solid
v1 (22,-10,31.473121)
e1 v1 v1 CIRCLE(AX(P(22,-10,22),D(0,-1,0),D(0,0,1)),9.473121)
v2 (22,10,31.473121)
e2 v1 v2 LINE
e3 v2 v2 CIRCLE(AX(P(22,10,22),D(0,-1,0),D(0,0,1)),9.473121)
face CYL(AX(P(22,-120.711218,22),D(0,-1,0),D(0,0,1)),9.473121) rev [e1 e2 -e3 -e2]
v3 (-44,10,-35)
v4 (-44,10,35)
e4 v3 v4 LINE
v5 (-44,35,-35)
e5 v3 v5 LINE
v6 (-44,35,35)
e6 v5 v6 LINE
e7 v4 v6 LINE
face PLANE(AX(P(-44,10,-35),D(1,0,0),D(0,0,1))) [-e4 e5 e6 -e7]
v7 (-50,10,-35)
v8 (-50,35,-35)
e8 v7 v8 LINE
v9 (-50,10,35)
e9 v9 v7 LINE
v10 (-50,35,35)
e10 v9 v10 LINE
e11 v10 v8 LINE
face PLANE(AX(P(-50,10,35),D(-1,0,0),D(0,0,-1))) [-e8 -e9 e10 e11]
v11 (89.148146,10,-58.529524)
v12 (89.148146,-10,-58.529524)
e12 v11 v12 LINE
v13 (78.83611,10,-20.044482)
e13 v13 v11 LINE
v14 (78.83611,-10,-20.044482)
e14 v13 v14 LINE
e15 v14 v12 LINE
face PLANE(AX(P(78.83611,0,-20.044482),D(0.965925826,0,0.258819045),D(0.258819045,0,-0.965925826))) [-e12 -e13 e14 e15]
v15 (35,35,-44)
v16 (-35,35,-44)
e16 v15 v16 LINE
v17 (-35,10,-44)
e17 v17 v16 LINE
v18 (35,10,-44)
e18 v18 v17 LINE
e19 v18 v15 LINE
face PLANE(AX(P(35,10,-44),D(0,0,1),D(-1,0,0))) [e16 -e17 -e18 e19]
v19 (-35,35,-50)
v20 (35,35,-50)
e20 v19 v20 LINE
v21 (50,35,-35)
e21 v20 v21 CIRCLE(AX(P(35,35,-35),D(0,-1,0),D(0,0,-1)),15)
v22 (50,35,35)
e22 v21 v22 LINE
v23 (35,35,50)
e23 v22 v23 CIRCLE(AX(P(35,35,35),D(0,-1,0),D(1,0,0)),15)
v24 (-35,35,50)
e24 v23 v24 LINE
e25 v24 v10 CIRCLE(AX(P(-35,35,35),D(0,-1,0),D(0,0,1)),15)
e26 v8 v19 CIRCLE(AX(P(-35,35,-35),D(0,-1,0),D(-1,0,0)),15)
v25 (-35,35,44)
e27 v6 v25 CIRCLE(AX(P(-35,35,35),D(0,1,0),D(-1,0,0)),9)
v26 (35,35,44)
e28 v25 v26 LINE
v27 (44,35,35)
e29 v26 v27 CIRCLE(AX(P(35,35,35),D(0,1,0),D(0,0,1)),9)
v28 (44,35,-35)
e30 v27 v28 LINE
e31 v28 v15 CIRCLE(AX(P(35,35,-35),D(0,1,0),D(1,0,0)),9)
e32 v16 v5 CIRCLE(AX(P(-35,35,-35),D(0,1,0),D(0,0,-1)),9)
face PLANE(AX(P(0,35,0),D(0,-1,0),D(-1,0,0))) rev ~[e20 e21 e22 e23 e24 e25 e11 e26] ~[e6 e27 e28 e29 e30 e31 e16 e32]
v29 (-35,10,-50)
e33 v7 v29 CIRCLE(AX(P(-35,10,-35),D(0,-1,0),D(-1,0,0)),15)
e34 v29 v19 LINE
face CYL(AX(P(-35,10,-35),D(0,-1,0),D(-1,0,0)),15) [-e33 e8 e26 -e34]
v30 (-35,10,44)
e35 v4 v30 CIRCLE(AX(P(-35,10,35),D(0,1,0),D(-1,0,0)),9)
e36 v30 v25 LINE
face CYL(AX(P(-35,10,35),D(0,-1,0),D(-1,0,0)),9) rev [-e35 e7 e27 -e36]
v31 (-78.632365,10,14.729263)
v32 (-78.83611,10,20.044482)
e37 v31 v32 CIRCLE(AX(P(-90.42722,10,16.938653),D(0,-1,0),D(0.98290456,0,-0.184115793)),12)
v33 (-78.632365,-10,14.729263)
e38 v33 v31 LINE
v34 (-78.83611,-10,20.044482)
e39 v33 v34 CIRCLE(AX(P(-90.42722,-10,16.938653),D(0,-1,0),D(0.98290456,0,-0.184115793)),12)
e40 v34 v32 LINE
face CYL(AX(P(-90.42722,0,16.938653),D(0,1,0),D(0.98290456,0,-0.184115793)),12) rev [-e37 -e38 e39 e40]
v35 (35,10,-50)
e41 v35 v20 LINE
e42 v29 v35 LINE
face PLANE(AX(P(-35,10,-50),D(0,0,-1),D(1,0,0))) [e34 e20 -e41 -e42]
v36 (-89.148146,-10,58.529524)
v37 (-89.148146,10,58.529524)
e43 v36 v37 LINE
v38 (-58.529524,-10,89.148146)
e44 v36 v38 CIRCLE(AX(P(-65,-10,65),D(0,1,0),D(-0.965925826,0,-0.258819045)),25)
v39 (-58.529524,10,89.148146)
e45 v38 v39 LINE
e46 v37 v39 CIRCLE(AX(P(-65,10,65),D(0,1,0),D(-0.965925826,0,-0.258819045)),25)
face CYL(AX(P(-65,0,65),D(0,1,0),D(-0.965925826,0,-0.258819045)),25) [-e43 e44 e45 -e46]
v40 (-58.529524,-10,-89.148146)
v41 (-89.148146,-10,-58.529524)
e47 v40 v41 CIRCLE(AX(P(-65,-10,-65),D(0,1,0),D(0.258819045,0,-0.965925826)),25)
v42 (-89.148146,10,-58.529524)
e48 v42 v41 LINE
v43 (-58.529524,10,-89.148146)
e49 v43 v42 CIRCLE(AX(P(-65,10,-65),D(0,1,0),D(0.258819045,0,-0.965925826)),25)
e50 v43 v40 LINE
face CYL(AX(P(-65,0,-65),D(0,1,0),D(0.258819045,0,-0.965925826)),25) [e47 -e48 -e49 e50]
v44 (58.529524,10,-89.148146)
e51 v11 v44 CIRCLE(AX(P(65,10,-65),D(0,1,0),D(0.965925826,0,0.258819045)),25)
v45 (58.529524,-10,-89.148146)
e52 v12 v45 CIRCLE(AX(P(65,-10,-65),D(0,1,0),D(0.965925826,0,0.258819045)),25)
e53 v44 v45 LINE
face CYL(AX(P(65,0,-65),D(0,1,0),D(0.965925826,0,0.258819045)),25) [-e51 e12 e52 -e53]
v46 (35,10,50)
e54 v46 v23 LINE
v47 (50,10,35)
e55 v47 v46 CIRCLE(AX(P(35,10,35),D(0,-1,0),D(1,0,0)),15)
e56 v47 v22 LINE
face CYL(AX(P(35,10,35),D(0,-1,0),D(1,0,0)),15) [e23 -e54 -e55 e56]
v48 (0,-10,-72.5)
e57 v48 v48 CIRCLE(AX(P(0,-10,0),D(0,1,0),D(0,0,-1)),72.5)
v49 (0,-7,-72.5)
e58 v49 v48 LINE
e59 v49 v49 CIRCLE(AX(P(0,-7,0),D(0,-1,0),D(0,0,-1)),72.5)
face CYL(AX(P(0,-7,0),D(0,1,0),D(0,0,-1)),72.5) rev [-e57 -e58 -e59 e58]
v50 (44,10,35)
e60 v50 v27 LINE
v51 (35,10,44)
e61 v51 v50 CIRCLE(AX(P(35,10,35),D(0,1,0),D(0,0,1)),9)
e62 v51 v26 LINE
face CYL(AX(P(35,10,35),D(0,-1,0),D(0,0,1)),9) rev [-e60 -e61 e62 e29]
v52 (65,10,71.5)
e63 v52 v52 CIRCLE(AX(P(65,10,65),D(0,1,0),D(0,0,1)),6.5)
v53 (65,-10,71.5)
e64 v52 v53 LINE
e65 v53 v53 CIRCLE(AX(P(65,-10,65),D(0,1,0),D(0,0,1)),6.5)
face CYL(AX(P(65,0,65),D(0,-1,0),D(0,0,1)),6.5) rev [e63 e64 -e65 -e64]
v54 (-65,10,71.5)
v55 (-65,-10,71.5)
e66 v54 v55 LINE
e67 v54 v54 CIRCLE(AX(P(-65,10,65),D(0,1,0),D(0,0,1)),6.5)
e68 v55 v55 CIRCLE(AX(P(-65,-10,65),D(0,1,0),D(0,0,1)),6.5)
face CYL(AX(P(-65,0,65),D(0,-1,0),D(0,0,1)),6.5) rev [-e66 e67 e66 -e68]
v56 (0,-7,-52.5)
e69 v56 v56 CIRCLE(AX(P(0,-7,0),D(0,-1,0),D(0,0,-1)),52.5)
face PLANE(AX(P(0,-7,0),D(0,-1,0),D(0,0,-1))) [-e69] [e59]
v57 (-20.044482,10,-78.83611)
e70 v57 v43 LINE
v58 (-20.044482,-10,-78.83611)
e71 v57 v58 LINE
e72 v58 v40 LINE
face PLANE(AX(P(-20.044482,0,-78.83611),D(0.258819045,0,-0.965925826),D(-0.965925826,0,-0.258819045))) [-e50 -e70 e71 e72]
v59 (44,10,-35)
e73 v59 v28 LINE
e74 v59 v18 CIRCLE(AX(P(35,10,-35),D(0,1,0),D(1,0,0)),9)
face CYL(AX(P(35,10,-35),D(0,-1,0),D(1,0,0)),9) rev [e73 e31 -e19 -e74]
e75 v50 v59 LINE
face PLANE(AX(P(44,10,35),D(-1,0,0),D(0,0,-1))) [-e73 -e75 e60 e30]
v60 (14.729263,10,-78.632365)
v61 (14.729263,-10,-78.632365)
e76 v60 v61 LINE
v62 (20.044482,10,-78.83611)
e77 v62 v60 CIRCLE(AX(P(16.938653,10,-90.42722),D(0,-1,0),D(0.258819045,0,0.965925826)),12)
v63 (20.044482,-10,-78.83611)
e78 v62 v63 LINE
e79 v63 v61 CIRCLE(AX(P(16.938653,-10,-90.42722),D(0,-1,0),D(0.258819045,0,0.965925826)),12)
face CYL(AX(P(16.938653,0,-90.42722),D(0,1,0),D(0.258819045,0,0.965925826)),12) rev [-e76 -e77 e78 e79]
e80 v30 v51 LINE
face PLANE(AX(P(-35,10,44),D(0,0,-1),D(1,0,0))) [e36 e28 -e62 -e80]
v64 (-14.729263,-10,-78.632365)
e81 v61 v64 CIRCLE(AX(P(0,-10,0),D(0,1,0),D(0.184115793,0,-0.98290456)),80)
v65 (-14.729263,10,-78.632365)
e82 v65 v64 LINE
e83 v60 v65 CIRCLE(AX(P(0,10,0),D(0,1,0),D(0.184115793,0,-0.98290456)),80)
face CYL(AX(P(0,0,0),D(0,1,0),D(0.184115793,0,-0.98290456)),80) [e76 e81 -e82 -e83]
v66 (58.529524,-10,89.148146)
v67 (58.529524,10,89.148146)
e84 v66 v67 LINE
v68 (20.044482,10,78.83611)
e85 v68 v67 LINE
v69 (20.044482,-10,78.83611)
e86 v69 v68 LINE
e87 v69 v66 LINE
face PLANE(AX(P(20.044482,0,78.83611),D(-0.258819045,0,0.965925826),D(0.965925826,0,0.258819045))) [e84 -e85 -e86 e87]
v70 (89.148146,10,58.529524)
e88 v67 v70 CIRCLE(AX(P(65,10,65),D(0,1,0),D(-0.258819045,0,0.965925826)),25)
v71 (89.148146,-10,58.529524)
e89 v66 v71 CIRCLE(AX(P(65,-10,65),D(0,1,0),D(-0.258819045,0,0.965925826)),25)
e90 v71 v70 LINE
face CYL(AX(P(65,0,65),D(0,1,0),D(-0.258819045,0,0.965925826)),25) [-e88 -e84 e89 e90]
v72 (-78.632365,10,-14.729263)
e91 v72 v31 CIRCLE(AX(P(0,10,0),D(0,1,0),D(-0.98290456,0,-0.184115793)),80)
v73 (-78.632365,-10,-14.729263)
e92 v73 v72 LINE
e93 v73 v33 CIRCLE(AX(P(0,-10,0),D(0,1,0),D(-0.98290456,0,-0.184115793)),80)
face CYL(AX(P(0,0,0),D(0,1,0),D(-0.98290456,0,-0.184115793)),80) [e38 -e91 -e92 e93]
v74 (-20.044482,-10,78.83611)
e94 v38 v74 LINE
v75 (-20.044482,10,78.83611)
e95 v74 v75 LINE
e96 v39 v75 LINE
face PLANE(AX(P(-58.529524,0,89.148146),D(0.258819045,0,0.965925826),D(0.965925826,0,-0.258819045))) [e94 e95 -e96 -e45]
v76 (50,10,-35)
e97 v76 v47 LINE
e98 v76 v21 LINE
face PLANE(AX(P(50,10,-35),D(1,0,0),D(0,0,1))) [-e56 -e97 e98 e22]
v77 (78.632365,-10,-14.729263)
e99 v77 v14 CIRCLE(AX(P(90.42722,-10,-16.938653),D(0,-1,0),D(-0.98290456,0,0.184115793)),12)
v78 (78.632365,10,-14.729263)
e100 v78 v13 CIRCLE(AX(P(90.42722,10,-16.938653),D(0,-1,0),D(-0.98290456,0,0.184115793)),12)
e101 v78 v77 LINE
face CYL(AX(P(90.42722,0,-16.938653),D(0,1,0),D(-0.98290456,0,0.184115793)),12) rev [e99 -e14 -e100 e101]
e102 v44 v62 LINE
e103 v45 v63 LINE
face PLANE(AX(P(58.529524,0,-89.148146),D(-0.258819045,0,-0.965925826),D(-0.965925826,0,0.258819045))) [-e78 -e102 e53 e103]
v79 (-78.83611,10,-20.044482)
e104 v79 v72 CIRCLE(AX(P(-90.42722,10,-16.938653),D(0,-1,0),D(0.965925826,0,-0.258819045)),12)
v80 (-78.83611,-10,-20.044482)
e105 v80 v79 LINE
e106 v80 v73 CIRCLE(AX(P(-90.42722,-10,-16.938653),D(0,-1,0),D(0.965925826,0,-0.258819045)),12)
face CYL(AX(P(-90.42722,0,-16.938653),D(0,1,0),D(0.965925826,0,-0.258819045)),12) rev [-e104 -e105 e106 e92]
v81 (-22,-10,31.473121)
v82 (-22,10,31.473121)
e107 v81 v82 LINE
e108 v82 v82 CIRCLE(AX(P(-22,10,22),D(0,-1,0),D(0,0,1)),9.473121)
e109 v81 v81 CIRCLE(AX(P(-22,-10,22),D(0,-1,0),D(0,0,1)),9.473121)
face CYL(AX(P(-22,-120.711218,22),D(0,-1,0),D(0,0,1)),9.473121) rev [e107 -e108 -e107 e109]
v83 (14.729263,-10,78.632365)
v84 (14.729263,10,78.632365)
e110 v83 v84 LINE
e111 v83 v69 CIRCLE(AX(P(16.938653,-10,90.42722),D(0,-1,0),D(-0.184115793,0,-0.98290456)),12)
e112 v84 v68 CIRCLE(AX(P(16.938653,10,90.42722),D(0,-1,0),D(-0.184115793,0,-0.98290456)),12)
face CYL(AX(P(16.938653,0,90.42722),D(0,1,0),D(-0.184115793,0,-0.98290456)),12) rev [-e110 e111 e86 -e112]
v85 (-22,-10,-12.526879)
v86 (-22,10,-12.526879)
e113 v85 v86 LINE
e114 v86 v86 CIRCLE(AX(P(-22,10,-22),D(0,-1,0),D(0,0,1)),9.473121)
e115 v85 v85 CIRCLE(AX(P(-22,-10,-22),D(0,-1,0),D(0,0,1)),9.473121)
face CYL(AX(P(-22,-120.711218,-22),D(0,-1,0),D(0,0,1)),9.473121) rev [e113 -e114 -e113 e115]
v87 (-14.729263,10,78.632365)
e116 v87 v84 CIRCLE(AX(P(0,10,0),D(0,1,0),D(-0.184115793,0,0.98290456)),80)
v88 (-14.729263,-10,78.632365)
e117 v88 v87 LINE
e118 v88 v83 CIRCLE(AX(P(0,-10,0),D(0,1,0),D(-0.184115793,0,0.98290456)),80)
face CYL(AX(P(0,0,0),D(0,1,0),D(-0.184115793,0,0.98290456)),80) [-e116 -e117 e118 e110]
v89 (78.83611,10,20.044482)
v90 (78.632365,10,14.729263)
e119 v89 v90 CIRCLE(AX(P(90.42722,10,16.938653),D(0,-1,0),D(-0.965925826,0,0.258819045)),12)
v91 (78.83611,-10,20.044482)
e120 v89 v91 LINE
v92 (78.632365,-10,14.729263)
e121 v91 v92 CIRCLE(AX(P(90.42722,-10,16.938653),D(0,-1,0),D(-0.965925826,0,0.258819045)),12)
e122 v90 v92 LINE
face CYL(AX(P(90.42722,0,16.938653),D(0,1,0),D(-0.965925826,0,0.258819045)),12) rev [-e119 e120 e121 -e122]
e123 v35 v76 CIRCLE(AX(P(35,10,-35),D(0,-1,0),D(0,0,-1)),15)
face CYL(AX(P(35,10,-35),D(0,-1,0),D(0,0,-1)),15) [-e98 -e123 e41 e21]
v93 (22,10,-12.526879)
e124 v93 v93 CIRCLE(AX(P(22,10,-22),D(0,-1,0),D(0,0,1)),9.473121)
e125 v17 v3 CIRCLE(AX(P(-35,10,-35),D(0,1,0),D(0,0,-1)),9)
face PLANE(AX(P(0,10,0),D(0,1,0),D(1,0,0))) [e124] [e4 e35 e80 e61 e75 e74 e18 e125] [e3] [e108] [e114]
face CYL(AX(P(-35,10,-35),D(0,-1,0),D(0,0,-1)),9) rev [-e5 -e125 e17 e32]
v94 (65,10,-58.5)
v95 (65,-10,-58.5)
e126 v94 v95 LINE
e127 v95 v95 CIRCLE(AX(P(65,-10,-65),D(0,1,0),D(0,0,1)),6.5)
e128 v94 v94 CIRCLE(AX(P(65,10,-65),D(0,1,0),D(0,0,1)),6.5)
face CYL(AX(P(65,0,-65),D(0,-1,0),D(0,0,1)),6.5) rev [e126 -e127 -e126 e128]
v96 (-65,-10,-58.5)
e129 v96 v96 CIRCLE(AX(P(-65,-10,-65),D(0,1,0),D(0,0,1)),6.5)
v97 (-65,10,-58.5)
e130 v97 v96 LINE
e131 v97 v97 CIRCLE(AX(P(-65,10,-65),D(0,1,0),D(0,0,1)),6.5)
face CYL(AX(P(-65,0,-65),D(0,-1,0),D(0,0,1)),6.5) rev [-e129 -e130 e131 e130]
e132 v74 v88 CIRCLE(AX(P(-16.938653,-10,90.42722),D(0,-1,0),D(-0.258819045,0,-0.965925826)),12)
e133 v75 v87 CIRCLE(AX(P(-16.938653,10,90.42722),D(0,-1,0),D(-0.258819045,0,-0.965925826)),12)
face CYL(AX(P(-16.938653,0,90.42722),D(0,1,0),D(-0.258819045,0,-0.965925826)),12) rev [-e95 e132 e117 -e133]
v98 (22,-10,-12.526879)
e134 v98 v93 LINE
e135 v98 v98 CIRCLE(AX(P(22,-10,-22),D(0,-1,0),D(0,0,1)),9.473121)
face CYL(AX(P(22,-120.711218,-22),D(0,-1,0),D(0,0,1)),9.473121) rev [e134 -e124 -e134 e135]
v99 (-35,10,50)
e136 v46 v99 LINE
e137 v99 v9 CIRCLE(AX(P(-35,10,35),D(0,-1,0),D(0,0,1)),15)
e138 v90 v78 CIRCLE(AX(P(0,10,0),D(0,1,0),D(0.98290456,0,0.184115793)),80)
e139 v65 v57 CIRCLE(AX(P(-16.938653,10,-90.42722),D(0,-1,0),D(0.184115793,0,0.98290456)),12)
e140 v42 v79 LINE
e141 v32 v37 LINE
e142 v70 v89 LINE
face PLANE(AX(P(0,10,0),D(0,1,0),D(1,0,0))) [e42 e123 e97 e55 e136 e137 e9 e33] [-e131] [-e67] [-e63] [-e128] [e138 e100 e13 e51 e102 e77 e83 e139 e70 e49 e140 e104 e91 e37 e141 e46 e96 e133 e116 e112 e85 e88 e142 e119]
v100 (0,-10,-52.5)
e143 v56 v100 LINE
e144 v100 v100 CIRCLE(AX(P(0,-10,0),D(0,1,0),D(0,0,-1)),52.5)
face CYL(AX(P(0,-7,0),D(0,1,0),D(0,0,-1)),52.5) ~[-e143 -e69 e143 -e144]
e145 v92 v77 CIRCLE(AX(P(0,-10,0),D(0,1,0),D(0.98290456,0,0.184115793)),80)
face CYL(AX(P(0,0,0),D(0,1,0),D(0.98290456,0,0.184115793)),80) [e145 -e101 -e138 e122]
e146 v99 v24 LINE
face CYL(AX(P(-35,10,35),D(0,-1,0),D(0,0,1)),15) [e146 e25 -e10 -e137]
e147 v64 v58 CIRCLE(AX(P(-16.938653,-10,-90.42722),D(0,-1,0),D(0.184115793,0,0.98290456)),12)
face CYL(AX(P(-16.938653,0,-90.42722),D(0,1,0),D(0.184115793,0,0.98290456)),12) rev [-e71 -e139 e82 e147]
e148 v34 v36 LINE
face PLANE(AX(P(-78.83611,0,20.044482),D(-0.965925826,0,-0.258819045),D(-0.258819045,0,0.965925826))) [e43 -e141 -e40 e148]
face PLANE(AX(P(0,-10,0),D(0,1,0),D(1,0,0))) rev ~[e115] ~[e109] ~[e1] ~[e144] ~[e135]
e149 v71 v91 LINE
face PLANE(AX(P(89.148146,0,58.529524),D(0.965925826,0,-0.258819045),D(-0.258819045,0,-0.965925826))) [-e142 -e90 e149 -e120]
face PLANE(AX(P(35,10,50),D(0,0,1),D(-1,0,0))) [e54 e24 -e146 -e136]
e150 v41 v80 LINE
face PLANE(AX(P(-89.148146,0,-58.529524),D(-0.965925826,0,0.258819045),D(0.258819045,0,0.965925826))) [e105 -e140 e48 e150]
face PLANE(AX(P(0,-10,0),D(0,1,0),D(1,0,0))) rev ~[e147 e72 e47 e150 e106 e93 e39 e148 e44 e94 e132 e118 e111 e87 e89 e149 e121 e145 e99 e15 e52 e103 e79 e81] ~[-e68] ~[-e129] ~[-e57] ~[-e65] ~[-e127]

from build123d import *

# Parameters (mm, degrees)
BASE_FLANGE_SKETCH_R      = 6.5
BASE_FLANGE_DEPTH         = 10
SQUARE_BOSS_DEPTH         = 25
BOSS_POCKET_DEPTH         = 130.711217711
BOSS_POCKET_DEPTH_BACK    = 130.711217711
BOSS_POCKET_SKETCH_R      = 9.473120825
RECESS_CUT_3MM_DEPTH      = 136
RECESS_CUT_3MM_DEPTH_BACK = 3
RECESS_SKETCH_R           = 72.5
RECESS_SKETCH_R_2         = 52.5


with BuildPart() as part:
    # Base Flange Sketch → Base Flange (new, symmetric)
    with BuildSketch(Plane(origin=(0, 0, 0), x_dir=(1, 0, 0), z_dir=(0, 1, 0))):
        with BuildLine():
            Line((-89.148145657, 58.529523872), (-78.836109635, 20.044481509))
            ThreePointArc((-78.836109635, 20.044481509), (-78.436026062, 17.398303615), (-78.632364827, 14.72926345))
            ThreePointArc((-78.632364827, 14.72926345), (-80, 0), (-78.632364827, -14.72926345))
            ThreePointArc((-78.632364827, -14.72926345), (-78.436026062, -17.398303615), (-78.836109635, -20.044481509))
            Line((-78.836109635, -20.044481509), (-89.148145657, -58.529523872))
            ThreePointArc((-89.148145657, -58.529523872), (-82.67766953, -82.67766953), (-58.529523872, -89.148145657))
            Line((-58.529523872, -89.148145657), (-20.044481509, -78.836109635))
            ThreePointArc((-20.044481509, -78.836109635), (-17.398303615, -78.436026062), (-14.72926345, -78.632364827))
            ThreePointArc((-14.72926345, -78.632364827), (0, -80), (14.72926345, -78.632364827))
            ThreePointArc((14.72926345, -78.632364827), (17.398303615, -78.436026062), (20.044481509, -78.836109635))
            Line((20.044481509, -78.836109635), (58.529523872, -89.148145657))
            ThreePointArc((58.529523872, -89.148145657), (82.67766953, -82.67766953), (89.148145657, -58.529523872))
            Line((89.148145657, -58.529523872), (78.836109635, -20.044481509))
            ThreePointArc((78.836109635, -20.044481509), (78.436026062, -17.398303615), (78.632364827, -14.72926345))
            ThreePointArc((78.632364827, -14.72926345), (80, 0), (78.632364827, 14.72926345))
            ThreePointArc((78.632364827, 14.72926345), (78.436026062, 17.398303615), (78.836109635, 20.044481509))
            Line((78.836109635, 20.044481509), (89.148145657, 58.529523872))
            ThreePointArc((89.148145657, 58.529523872), (82.67766953, 82.67766953), (58.529523872, 89.148145657))
            Line((58.529523872, 89.148145657), (20.044481509, 78.836109635))
            ThreePointArc((20.044481509, 78.836109635), (17.398303615, 78.436026062), (14.72926345, 78.632364827))
            ThreePointArc((14.72926345, 78.632364827), (0, 80), (-14.72926345, 78.632364827))
            ThreePointArc((-14.72926345, 78.632364827), (-17.398303615, 78.436026062), (-20.044481509, 78.836109635))
            Line((-20.044481509, 78.836109635), (-58.529523872, 89.148145657))
            ThreePointArc((-58.529523872, 89.148145657), (-82.67766953, 82.67766953), (-89.148145657, 58.529523872))
        make_face()
        with Locations(Location((-65, 65, 0), (0, 0, 270))):
            Circle(BASE_FLANGE_SKETCH_R, mode=Mode.SUBTRACT)
        with Locations(Location((65, 65, 0), (0, 0, 270))):
            Circle(BASE_FLANGE_SKETCH_R, mode=Mode.SUBTRACT)
        with Locations(Location((65, -65, 0), (0, 0, 270))):
            Circle(BASE_FLANGE_SKETCH_R, mode=Mode.SUBTRACT)
        with Locations(Location((-65, -65, 0), (0, 0, 270))):
            Circle(BASE_FLANGE_SKETCH_R, mode=Mode.SUBTRACT)
    extrude(amount=BASE_FLANGE_DEPTH, both=True)

    # Square Boss Sketch → Square Boss (add)
    with BuildSketch(Plane(origin=(0, 10, 0), x_dir=(1, 0, 0), z_dir=(0, 1, 0))):
        with BuildLine():
            Line((-35, 50), (35, 50))
            ThreePointArc((35, 50), (45.606601718, 45.606601718), (50, 35))
            Line((50, 35), (50, -35))
            ThreePointArc((50, -35), (45.606601718, -45.606601718), (35, -50))
            Line((35, -50), (-35, -50))
            ThreePointArc((-35, -50), (-45.606601718, -45.606601718), (-50, -35))
            Line((-50, -35), (-50, 35))
            ThreePointArc((-50, 35), (-45.606601718, 45.606601718), (-35, 50))
        make_face()
        with BuildLine():
            ThreePointArc((-35, 44), (-41.363961031, 41.363961031), (-44, 35))
            Line((-44, 35), (-44, -35))
            ThreePointArc((-44, -35), (-41.363961031, -41.363961031), (-35, -44))
            Line((-35, -44), (35, -44))
            ThreePointArc((35, -44), (41.363961031, -41.363961031), (44, -35))
            Line((44, -35), (44, 35))
            ThreePointArc((44, 35), (41.363961031, 41.363961031), (35, 44))
            Line((35, 44), (-35, 44))
        make_face(mode=Mode.SUBTRACT)
    extrude(amount=SQUARE_BOSS_DEPTH)

    # Boss Pocket Sketch → Boss Pocket (cut, two sides: drawn at the far end of the back side and taken through both)
    with BuildSketch(Plane(origin=(0, 10, 0), x_dir=(1, 0, 0), z_dir=(0, 1, 0)).offset(-BOSS_POCKET_DEPTH_BACK)):
        with Locations(Location((-22, -22, 0), (0, 0, 270))):
            Circle(BOSS_POCKET_SKETCH_R)
        with Locations(Location((22, -22, 0), (0, 0, 270))):
            Circle(BOSS_POCKET_SKETCH_R)
        with Locations(Location((22, 22, 0), (0, 0, 270))):
            Circle(BOSS_POCKET_SKETCH_R)
        with Locations(Location((-22, 22, 0), (0, 0, 270))):
            Circle(BOSS_POCKET_SKETCH_R)
    extrude(amount=BOSS_POCKET_DEPTH + BOSS_POCKET_DEPTH_BACK, mode=Mode.SUBTRACT)

    # Recess Sketch → Recess Cut 3mm (cut, two sides: drawn at the far end of the back side and taken through both)
    with BuildSketch(Plane.XZ.offset(10).offset(-RECESS_CUT_3MM_DEPTH_BACK)):
        with Locations(Location((0, 0, 0), (0, 0, 270))):
            Circle(RECESS_SKETCH_R)
        with Locations(Location((0, 0, 0), (0, 0, 270))):
            Circle(RECESS_SKETCH_R_2, mode=Mode.SUBTRACT)
    extrude(amount=RECESS_CUT_3MM_DEPTH + RECESS_CUT_3MM_DEPTH_BACK, mode=Mode.SUBTRACT)


solid = part.part
